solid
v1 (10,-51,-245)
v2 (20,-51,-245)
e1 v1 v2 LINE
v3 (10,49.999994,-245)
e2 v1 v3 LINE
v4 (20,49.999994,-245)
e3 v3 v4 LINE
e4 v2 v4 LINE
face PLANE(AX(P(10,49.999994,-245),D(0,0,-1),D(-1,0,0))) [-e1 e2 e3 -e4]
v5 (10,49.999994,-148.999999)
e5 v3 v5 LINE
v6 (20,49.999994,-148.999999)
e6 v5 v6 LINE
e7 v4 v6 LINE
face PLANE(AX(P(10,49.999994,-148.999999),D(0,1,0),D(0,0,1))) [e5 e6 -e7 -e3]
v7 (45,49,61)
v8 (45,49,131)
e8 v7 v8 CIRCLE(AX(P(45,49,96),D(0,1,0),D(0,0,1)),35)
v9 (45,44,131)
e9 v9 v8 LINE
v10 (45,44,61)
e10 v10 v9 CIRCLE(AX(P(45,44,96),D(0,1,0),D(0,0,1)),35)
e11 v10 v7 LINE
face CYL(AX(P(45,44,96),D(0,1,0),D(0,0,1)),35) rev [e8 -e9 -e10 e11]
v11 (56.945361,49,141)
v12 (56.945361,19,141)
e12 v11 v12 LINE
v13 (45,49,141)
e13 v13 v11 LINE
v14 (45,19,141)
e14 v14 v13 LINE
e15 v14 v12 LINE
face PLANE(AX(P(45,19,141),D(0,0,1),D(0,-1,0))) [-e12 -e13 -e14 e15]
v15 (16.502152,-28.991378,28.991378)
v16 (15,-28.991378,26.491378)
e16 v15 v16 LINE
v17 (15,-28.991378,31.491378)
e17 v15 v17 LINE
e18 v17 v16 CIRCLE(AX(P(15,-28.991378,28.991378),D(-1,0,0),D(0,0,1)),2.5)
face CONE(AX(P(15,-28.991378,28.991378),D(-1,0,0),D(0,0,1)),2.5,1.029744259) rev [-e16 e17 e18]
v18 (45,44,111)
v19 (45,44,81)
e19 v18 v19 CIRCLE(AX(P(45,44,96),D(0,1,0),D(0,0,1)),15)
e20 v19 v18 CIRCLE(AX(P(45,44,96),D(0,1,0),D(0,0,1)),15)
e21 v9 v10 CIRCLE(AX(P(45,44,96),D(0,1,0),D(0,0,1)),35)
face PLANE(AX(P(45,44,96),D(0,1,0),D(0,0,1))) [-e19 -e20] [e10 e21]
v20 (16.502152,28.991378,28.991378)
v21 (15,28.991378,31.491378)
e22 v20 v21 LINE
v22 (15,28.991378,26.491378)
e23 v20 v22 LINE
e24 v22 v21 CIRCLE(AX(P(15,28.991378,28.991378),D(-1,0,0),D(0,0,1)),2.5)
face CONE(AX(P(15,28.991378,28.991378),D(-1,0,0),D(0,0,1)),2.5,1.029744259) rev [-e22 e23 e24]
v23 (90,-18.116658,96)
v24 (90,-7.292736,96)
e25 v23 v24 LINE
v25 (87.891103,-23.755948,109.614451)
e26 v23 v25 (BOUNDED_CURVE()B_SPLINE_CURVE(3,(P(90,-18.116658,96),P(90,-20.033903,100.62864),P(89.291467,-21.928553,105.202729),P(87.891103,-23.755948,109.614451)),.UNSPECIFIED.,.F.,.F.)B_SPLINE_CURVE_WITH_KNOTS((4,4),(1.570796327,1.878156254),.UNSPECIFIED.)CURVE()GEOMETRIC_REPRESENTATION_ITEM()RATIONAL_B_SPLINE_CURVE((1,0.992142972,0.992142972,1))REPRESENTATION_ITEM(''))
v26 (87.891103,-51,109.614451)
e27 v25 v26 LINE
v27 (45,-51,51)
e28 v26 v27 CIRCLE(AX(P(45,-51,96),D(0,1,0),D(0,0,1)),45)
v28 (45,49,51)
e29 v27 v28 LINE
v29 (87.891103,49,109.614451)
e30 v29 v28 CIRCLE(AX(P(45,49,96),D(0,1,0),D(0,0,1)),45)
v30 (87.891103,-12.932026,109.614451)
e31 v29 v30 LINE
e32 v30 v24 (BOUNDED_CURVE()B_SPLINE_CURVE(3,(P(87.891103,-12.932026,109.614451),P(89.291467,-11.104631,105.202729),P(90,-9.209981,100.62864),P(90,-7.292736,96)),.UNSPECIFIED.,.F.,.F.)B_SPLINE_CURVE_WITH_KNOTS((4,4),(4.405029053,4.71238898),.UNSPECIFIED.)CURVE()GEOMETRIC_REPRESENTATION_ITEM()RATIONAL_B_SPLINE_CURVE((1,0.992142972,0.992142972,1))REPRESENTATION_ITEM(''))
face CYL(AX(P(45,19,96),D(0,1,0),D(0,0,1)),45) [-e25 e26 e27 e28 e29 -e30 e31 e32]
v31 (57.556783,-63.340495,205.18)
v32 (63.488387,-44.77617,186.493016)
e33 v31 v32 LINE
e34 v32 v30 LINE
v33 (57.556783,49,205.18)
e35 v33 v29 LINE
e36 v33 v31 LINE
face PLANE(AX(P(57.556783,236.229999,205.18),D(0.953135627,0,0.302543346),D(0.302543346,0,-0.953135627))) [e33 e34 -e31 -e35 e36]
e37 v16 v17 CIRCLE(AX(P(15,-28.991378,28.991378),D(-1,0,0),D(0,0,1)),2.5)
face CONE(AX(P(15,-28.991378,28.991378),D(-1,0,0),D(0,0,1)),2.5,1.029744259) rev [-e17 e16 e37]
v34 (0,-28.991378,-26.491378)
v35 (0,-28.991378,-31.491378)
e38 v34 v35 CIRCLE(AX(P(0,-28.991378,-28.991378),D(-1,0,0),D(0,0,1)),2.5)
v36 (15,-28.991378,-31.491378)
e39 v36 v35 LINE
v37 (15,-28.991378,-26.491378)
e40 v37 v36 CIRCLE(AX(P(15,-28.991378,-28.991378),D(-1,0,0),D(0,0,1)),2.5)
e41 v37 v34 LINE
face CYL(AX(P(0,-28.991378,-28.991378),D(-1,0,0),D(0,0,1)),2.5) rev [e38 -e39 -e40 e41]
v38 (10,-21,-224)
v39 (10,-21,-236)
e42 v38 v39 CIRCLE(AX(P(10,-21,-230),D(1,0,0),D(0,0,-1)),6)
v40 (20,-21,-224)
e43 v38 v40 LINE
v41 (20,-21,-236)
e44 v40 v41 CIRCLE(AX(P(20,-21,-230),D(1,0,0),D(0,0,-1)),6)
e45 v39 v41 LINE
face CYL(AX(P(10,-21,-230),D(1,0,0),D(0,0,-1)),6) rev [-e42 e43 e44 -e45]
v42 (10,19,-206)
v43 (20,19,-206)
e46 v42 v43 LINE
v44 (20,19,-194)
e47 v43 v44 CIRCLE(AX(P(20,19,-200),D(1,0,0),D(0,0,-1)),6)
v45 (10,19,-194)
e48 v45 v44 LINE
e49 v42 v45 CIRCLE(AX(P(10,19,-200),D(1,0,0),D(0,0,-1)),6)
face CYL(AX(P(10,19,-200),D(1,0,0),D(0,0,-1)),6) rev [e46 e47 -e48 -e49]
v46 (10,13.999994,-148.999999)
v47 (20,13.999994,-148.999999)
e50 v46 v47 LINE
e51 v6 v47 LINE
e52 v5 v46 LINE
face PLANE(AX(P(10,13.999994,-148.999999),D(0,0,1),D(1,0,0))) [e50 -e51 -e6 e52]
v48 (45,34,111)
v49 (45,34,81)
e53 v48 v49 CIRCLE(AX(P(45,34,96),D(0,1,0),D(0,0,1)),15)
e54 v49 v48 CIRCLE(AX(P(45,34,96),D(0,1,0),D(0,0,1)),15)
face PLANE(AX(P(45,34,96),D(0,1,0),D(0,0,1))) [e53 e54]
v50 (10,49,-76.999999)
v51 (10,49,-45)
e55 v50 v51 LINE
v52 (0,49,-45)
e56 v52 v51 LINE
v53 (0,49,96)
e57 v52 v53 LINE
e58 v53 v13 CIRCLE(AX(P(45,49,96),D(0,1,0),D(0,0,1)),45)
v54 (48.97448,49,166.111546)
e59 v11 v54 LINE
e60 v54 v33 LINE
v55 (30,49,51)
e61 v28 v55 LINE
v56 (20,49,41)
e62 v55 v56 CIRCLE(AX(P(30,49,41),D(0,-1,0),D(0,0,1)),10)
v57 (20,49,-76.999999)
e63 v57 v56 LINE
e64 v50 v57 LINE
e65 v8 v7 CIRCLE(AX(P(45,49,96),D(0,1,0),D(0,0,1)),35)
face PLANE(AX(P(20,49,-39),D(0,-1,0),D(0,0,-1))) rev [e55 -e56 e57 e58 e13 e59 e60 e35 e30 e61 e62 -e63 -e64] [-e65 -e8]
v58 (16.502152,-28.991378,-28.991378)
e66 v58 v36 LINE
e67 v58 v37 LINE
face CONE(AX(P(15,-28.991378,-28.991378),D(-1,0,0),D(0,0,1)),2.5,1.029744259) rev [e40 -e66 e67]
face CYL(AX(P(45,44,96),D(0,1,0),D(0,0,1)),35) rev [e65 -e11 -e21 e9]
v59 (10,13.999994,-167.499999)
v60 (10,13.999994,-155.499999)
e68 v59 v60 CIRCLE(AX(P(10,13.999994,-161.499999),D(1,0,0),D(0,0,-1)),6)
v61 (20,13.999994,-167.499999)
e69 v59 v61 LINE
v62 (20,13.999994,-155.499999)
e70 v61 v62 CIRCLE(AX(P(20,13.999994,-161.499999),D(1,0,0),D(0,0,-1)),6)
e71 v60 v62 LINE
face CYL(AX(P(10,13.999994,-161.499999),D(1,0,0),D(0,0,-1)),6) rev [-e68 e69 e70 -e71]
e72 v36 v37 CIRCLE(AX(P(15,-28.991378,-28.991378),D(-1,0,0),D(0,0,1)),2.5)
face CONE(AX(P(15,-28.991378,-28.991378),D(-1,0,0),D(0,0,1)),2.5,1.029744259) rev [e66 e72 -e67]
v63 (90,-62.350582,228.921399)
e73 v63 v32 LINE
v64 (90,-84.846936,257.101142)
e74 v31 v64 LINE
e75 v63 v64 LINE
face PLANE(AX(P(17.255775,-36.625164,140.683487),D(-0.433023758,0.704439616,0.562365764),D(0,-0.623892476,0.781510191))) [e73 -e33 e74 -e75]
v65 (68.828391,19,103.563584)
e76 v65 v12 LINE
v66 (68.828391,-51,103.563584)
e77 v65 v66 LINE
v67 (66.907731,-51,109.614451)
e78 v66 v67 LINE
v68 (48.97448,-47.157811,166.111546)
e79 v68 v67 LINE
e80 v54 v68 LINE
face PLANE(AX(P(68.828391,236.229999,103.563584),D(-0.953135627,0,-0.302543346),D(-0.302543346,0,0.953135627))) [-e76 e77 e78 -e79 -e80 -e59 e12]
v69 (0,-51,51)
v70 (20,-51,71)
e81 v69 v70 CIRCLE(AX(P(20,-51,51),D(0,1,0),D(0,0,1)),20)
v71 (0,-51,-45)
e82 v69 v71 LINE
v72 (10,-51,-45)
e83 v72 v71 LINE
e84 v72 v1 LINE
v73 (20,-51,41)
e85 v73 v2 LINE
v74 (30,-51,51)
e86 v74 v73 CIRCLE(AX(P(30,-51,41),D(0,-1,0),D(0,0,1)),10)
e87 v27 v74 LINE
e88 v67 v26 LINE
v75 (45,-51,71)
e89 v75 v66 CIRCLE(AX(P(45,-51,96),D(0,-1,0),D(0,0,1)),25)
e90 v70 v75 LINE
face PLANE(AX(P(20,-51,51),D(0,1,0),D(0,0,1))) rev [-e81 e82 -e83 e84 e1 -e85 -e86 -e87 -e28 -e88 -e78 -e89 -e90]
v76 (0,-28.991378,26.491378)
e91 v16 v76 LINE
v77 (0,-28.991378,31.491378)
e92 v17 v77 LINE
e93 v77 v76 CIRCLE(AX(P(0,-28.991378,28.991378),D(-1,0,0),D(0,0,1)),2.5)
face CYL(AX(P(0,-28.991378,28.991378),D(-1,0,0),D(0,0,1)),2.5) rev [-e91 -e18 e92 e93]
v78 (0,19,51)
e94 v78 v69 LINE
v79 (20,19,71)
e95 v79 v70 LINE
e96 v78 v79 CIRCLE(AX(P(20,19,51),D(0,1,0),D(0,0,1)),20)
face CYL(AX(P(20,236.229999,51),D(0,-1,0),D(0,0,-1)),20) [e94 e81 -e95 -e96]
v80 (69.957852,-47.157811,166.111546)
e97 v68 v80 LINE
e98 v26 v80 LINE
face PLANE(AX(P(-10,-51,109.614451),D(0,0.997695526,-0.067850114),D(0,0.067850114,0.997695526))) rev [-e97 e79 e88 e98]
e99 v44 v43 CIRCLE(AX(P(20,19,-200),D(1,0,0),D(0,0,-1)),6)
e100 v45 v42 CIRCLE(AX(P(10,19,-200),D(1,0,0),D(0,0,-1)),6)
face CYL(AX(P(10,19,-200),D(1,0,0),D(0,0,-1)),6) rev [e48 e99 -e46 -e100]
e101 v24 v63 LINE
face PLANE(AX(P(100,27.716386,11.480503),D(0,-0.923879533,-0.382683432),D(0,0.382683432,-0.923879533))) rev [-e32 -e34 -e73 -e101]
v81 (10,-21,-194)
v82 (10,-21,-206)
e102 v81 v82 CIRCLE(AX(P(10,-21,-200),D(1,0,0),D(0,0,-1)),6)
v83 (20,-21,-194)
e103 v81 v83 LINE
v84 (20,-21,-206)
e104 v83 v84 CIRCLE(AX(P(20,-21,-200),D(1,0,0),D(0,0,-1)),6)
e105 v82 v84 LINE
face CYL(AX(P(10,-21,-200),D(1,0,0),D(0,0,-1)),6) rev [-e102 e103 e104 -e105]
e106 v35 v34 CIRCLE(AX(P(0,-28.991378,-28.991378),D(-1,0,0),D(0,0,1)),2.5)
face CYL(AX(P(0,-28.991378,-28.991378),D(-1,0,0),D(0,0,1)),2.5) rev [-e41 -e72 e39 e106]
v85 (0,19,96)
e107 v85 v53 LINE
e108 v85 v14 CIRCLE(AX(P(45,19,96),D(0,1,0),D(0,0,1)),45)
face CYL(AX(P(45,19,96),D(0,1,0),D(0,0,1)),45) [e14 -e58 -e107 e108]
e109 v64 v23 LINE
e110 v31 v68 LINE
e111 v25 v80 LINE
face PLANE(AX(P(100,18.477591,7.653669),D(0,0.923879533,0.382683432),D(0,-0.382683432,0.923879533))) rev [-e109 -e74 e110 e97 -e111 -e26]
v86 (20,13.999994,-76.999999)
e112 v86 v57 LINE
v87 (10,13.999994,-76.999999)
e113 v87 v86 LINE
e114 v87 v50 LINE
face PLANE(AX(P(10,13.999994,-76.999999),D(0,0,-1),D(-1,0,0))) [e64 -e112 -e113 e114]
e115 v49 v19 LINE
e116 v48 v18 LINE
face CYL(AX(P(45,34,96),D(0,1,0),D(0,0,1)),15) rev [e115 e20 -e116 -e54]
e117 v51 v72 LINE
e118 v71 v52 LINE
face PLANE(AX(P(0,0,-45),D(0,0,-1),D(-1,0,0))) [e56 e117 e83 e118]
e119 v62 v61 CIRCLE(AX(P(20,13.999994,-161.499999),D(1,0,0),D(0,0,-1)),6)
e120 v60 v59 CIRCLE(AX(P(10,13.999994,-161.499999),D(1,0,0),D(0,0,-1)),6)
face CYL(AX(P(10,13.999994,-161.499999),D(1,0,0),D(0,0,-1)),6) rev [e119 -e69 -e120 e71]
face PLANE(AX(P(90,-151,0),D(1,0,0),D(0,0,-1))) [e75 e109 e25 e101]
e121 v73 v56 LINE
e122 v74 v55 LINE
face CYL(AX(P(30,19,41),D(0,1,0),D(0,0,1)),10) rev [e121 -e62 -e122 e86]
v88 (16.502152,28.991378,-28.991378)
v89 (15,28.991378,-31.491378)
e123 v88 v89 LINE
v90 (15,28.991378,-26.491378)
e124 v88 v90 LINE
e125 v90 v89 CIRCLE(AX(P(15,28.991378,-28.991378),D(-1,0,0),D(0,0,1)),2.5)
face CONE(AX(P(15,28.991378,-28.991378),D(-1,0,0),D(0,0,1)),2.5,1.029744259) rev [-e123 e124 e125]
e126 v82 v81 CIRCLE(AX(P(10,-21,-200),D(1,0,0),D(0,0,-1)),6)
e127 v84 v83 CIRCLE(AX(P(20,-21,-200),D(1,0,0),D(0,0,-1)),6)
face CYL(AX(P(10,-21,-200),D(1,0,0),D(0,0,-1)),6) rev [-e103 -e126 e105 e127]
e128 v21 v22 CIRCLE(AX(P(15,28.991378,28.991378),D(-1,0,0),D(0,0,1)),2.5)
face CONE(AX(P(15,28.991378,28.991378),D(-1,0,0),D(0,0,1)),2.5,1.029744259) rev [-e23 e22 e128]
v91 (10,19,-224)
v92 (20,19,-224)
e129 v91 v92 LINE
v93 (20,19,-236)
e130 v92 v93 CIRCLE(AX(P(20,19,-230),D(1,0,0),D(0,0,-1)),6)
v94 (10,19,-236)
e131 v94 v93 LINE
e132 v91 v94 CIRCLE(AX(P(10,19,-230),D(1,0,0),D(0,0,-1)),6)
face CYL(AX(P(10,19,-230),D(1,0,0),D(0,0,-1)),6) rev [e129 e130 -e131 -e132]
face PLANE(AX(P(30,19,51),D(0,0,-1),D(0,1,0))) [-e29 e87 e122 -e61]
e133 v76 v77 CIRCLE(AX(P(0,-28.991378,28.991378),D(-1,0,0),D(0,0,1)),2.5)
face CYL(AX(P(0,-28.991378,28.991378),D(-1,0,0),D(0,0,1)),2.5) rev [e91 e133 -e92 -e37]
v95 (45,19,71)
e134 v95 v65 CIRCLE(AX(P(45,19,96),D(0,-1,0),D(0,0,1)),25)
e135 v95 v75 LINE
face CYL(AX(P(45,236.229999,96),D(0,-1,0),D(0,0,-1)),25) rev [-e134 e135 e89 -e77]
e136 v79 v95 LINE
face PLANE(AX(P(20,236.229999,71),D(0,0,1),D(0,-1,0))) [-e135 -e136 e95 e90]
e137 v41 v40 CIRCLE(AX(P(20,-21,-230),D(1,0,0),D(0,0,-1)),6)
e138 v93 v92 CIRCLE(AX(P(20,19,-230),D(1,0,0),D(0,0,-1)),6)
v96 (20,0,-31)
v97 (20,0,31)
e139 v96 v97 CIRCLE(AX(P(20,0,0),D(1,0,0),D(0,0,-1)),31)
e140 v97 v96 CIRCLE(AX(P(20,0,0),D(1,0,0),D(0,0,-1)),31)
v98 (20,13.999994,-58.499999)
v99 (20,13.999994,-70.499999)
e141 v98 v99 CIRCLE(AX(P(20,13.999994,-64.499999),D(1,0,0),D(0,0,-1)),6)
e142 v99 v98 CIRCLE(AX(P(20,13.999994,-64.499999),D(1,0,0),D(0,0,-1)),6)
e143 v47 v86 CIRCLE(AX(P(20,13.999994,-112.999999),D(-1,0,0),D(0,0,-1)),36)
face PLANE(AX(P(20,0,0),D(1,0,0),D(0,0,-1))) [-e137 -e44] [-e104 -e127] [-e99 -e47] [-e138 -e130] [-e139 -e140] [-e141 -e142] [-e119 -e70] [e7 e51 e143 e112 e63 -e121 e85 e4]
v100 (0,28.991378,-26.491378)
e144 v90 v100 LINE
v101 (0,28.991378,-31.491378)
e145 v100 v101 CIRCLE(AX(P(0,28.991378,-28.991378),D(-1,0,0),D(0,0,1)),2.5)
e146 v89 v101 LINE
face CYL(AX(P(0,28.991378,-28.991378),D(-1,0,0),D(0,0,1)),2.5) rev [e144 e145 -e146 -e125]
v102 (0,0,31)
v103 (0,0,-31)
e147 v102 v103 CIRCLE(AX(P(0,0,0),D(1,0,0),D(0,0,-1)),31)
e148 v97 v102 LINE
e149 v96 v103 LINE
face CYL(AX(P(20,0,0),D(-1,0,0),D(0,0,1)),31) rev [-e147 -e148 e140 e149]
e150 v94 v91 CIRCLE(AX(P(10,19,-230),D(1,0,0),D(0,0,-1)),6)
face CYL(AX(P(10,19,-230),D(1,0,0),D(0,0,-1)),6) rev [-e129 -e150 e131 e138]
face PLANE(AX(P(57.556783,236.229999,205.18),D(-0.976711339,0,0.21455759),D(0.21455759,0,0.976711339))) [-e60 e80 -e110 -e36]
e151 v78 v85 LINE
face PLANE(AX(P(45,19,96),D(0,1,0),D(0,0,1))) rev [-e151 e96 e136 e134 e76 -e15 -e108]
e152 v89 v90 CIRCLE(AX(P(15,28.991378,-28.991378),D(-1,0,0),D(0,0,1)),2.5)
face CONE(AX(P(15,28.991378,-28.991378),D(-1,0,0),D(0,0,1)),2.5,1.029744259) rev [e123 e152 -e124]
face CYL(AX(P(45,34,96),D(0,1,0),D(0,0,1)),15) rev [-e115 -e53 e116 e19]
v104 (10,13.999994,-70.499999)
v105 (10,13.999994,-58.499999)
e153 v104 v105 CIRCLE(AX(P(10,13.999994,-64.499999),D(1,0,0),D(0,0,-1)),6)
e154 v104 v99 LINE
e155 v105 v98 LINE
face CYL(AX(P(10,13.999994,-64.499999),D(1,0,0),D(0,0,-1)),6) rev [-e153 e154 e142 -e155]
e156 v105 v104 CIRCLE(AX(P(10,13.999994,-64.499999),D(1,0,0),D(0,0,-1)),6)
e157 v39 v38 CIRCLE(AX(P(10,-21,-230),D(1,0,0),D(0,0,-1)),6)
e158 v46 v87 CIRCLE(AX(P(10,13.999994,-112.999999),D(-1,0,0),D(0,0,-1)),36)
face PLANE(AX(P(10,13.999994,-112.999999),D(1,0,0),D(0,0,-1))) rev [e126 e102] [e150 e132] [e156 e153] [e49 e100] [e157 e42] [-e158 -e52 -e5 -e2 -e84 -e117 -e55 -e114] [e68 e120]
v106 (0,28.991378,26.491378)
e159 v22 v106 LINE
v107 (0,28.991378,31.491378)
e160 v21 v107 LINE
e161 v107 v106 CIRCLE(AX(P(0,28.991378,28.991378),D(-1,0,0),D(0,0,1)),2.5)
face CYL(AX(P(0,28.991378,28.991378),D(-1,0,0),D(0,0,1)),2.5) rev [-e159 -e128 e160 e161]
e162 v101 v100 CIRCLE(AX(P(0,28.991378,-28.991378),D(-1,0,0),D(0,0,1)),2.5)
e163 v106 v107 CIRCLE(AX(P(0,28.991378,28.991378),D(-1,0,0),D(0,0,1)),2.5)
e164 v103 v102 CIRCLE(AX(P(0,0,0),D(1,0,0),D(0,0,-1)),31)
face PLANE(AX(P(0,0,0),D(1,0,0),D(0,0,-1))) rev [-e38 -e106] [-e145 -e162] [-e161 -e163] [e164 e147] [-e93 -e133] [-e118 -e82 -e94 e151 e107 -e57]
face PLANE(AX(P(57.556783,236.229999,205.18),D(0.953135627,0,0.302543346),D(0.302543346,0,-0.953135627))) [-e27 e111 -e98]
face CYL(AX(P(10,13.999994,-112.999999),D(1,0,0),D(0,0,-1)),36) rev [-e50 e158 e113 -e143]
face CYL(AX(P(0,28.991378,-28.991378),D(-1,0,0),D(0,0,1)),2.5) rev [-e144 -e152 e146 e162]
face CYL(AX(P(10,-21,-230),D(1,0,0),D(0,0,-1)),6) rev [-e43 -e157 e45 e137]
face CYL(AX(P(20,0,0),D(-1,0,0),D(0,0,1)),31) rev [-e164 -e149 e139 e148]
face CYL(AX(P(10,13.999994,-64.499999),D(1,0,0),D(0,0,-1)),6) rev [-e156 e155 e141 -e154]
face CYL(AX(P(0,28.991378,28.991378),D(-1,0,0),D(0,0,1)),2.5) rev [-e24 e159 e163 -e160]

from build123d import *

# Parameters (mm, degrees)
SKETCH_1_W                  = 90
SKETCH_1_H                  = 100
SKETCH_1_R                  = 31
EXTRUDE_1_DEPTH             = 20
EXTRUDE_2_DEPTH             = 30
EXTRUDE_3_REACH             = 183.331
EXTRUDE_3_DIRECTION_2_REACH = 183.331
EXTRUDE_4_DEPTH             = 100
CUT_EXTRUDE_1_DEPTH         = 100
CUT_EXTRUDE_1_DEPTH_BACK    = 70
CUT_EXTRUDE_2_DEPTH         = 100
EXTRUDE_6_REACH             = 292.174
CUT_EXTRUDE_3_REACH         = 339.181
SKETCH_9_R                  = 35
CUT_EXTRUDE_4_DEPTH         = 5
SKETCH_10_R                 = 15
CUT_EXTRUDE_5_DEPTH         = 10
HOLE_WIZARD_M6_1_D          = 5
HOLE_WIZARD_M6_1_DEPTH      = 15
HOLE_WIZARD_M6_1_TIP        = 1.502151548
SKETCH_15_W                 = 20
SKETCH_15_H                 = 100
EXTRUDE_7_DEPTH             = 6
SKETCH_16_R                 = 6
EXTRUDE_8_DEPTH             = 10


with BuildPart() as part:
    # 草图1 → 凸台-拉伸1 (new body)
    with BuildSketch(Plane(origin=(0, 0, 0), x_dir=(0, 0, -1), z_dir=(1, 0, 0))):
        with Locations((-6, -1)):
            Rectangle(SKETCH_1_W, SKETCH_1_H)
        Circle(SKETCH_1_R, mode=Mode.SUBTRACT)
    extrude(amount=EXTRUDE_1_DEPTH)

    # 草图2 → 凸台-拉伸2 (add)
    with BuildSketch(Plane(origin=(0, 49, 0), x_dir=(1, 0, 0), z_dir=(0, 1, 0))):
        with BuildLine():
            Line((0, -51), (0, -96))
            ThreePointArc((0, -96), (13.180194847, -127.819805153), (45, -141))
            Line((45, -141), (76.819805153, -141))
            Line((76.819805153, -141), (76.819805153, -127.819805153))
            ThreePointArc((76.819805153, -127.819805153), (86.574578963, -78.779245544), (45, -51))
            Line((45, -51), (30, -51))
            ThreePointArc((30, -51), (22.928932188, -48.071067812), (20, -41))
            Line((20, -41), (0, -41))
            Line((0, -41), (0, -51))
        make_face()
    extrude(amount=-EXTRUDE_2_DEPTH)

    # 凸台-拉伸3: up to this face of the body (flat: up to its plane)
    extrude_3_end = Plane(part.part.faces().sort_by_distance((36.366131186, 49, 76.243712536))[0])
    # 草图3 → 凸台-拉伸3 (add, up to the picked face)
    with BuildSketch(Plane.XZ.offset(-19), mode=Mode.PRIVATE) as extrude_3_sk1:
        with BuildLine():
            Line((20, 71), (45, 71))
            ThreePointArc((45, 71), (65.17535119, 81.23669399), (68.828390679, 103.563583652))
            Line((68.828390679, 103.563583652), (48.974479643, 166.111546424))
            Line((48.974479643, 166.111546424), (57.556783249, 205.18))
            Line((57.556783249, 205.18), (87.891103222, 109.614450573))
            ThreePointArc((87.891103222, 109.614450573), (81.315632142, 69.426049181), (45, 51))
            Line((45, 51), (40, 51))
            Line((40, 51), (30, 51))
            ThreePointArc((30, 51), (22.928932188, 48.071067812), (20, 41))
            Line((20, 41), (0, 41))
            Line((0, 41), (0, 51))
            ThreePointArc((0, 51), (5.857864376, 65.142135624), (20, 71))
        make_face()
    extrude_3_tool1 = split(extrude(extrude_3_sk1.sketch, amount=-EXTRUDE_3_REACH, mode=Mode.PRIVATE), bisect_by=extrude_3_end, keep=Keep.BOTH, mode=Mode.PRIVATE)
    add(extrude_3_tool1.solids().sort_by(Axis((7.18178, 19, 63.81822), (0, 1, 0)))[0])

    # 凸台-拉伸3 direction 2: up to this face of the body (flat: up to its plane)
    extrude_3_direction_2_end = Plane(part.part.faces().sort_by_distance((10, -51, 6))[0])
    # 草图3 → 凸台-拉伸3 direction 2 (add, up to the picked face)
    with BuildSketch(Plane.XZ.offset(-19), mode=Mode.PRIVATE) as extrude_3_direction_2_sk1:
        with BuildLine():
            Line((20, 71), (45, 71))
            ThreePointArc((45, 71), (65.17535119, 81.23669399), (68.828390679, 103.563583652))
            Line((68.828390679, 103.563583652), (48.974479643, 166.111546424))
            Line((48.974479643, 166.111546424), (57.556783249, 205.18))
            Line((57.556783249, 205.18), (87.891103222, 109.614450573))
            ThreePointArc((87.891103222, 109.614450573), (81.315632142, 69.426049181), (45, 51))
            Line((45, 51), (40, 51))
            Line((40, 51), (30, 51))
            ThreePointArc((30, 51), (22.928932188, 48.071067812), (20, 41))
            Line((20, 41), (0, 41))
            Line((0, 41), (0, 51))
            ThreePointArc((0, 51), (5.857864376, 65.142135624), (20, 71))
        make_face()
    extrude_3_direction_2_tool1 = split(extrude(extrude_3_direction_2_sk1.sketch, amount=EXTRUDE_3_DIRECTION_2_REACH, mode=Mode.PRIVATE), bisect_by=extrude_3_direction_2_end, keep=Keep.BOTH, mode=Mode.PRIVATE)
    add(extrude_3_direction_2_tool1.solids().sort_by(Axis((7.18178, 19, 63.81822), (0, -1, 0)))[0])

    # 草图4 → 凸台-拉伸4 (add)
    with BuildSketch(Plane.ZY):
        Polygon((79.044272811, -11.09336582), (82.871107135, -1.854570495), (260.927976749, -75.608140763), (257.101142425, -84.846936088), align=None)
    extrude(amount=-EXTRUDE_4_DEPTH)

    # 草图5 → 切除-拉伸1 (cut, two sides: drawn at the far end of the back side and taken through both)
    with BuildSketch(Plane.XZ.offset(51).offset(-CUT_EXTRUDE_1_DEPTH_BACK)):
        with BuildLine():
            Line((90, 273.997870748), (90, 257.101142425))
            Line((90, 257.101142425), (90, 96))
            ThreePointArc((90, 96), (89.163059449, 87.361471182), (86.683369771, 79.044272811))
            Line((86.683369771, 79.044272811), (109.692797529, 79.044272811))
            Line((109.692797529, 79.044272811), (210.132802407, 79.044272811))
            Line((210.132802407, 79.044272811), (210.132802407, 273.997870748))
            Line((210.132802407, 273.997870748), (90, 273.997870748))
        make_face()
        with BuildLine():
            Line((-30.73238043, 79.044272811), (63.371263307, 79.044272811))
            ThreePointArc((63.371263307, 79.044272811), (69.402906592, 90.568780078), (68.828390679, 103.563583652))
            Line((68.828390679, 103.563583652), (48.974479643, 166.111546424))
            Line((48.974479643, 166.111546424), (51.012141043, 175.387410276))
            Line((51.012141043, 175.387410276), (57.556783249, 205.18))
            Line((57.556783249, 205.18), (90, 257.101142425))
            Line((90, 257.101142425), (-30.73238043, 295.986256779))
            Line((-30.73238043, 295.986256779), (-30.73238043, 79.044272811))
        make_face()
    extrude(amount=CUT_EXTRUDE_1_DEPTH + CUT_EXTRUDE_1_DEPTH_BACK, mode=Mode.SUBTRACT)


with BuildPart() as body_2:
    # of the pieces the cut leaves, the one that is kept (cut_extrude_1_keep)
    add(part.part.solids().sort_by_distance((0, 49, 96))[0])

    # 草图6 → 切除-拉伸2 (cut)
    with BuildSketch(Plane(origin=(90, 0, 0), x_dir=(0, 0, -1), z_dir=(1, 0, 0))):
        Polygon((-109.614450573, -51), (-166.111546424, -47.15781139), (-175.387410276, -51), align=None)
    extrude(amount=-CUT_EXTRUDE_2_DEPTH, mode=Mode.SUBTRACT)

    # 凸台-拉伸6: up to this face of the body (flat: up to its plane)
    extrude_6_end = Plane(body_2.part.faces().sort_by_distance((79.164953254, -45.54677493, 188.353419651))[0])
    # 草图7 → 凸台-拉伸6 (add, up to the picked face)
    with BuildSketch(Plane.XZ.offset(51), mode=Mode.PRIVATE) as extrude_6_sk1:
        Polygon((57.556783249, 205.18), (58.718959047, 201.518669574), (56.75248601, 201.518669574), align=None)
    extrude_6_tool1 = split(extrude(extrude_6_sk1.sketch, amount=EXTRUDE_6_REACH, mode=Mode.PRIVATE), bisect_by=extrude_6_end, keep=Keep.BOTH, mode=Mode.PRIVATE)
    add(extrude_6_tool1.solids().sort_by(Axis((57.676076, -51, 202.739113), (0, -1, 0)))[0])

    # 切除-拉伸3: up to this plane
    cut_extrude_3_end = Plane(origin=(57.556783249, 236.229998665, 205.18), z_dir=(0.9531356271558171, 0, 0.3025433460618284))
    # 草图8 → 切除-拉伸3 (cut, up to the surface)
    with BuildSketch(Plane(origin=(90, -84.846936088, 257.101142425), x_dir=(-0.8660475161032836, -0.19132705878879122, 0.46190438017685376), z_dir=(-0.4999616983843192, 0.3314220360536652, -0.8001235743100625)), mode=Mode.PRIVATE) as cut_extrude_3_sk1:
        Polygon((0, 0), (-39.725764101, 22.935680597), (0, 22.935680597), align=None)
    cut_extrude_3_tool1 = split(extrude(cut_extrude_3_sk1.sketch, amount=CUT_EXTRUDE_3_REACH, mode=Mode.PRIVATE), bisect_by=cut_extrude_3_end, keep=Keep.BOTH, mode=Mode.PRIVATE)
    add(cut_extrude_3_tool1.solids().sort_by_distance((101.468133, -68.186861, 256.836044))[0], mode=Mode.SUBTRACT)

    # 草图9 → 切除-拉伸4 (cut)
    with BuildSketch(Plane(origin=(0, 49, 0), x_dir=(1, 0, 0), z_dir=(0, 1, 0))):
        with Locations(Location((45, -96, 0), (0, 0, 270))):
            Circle(SKETCH_9_R)
    extrude(amount=-CUT_EXTRUDE_4_DEPTH, mode=Mode.SUBTRACT)

    # 草图10 → 切除-拉伸5 (cut)
    with BuildSketch(Plane(origin=(0, 44, 0), x_dir=(1, 0, 0), z_dir=(0, 1, 0))):
        with Locations(Location((45, -96, 0), (0, 0, 270))):
            Circle(SKETCH_10_R)
    extrude(amount=-CUT_EXTRUDE_5_DEPTH, mode=Mode.SUBTRACT)

    # M6 螺纹孔1
    with Locations(Plane.ZY):
        with Locations((28.991378029, 28.991378029), (-28.991378029, 28.991378029), (-28.991378029, -28.991378029), (28.991378029, -28.991378029)):
            Hole(HOLE_WIZARD_M6_1_D / 2, depth=HOLE_WIZARD_M6_1_DEPTH)
            with Locations((0, 0, -(HOLE_WIZARD_M6_1_DEPTH + HOLE_WIZARD_M6_1_TIP / 2))):  # 118° drill point
                Cone(0, HOLE_WIZARD_M6_1_D / 2, HOLE_WIZARD_M6_1_TIP, mode=Mode.SUBTRACT)

    # 草图15 → 凸台-拉伸7 (add)
    with BuildSketch(Plane(origin=(0, 0, -39), x_dir=(-1, 0, 0), z_dir=(0, 0, -1))):
        with Locations((-10, -1)):
            Rectangle(SKETCH_15_W, SKETCH_15_H)
    extrude(amount=EXTRUDE_7_DEPTH)

    # 草图16 → 凸台-拉伸8 (add)
    with BuildSketch(Plane(origin=(20, 0, 0), x_dir=(0, 0, -1), z_dir=(1, 0, 0))):
        with BuildLine():
            Line((45, -51), (73, -51))
            Line((73, -51), (245, -51))
            Line((245, -51), (245, 49.999994373))
            Line((245, 49.999994373), (148.999999307, 49.999994373))
            Line((148.999999307, 49.999994373), (148.999999307, 13.999994373))
            ThreePointArc((148.999999307, 13.999994373), (112.999999307, -22.000005627), (76.999999307, 13.999994373))
            Line((76.999999307, 13.999994373), (76.999999307, 49))
            Line((76.999999307, 49), (73, 49))
            Line((73, 49), (45, 49))
            Line((45, 49), (45, -51))
        make_face()
        with Locations((230, 19)):
            Circle(SKETCH_16_R, mode=Mode.SUBTRACT)
        with Locations((200, 19)):
            Circle(SKETCH_16_R, mode=Mode.SUBTRACT)
        with Locations((230, -21)):
            Circle(SKETCH_16_R, mode=Mode.SUBTRACT)
        with Locations((200, -21)):
            Circle(SKETCH_16_R, mode=Mode.SUBTRACT)
        with Locations((161.499999307, 13.999994373)):
            Circle(SKETCH_16_R, mode=Mode.SUBTRACT)
        with Locations((64.499999307, 13.999994373)):
            Circle(SKETCH_16_R, mode=Mode.SUBTRACT)
    extrude(amount=-EXTRUDE_8_DEPTH)


solid = body_2.part
